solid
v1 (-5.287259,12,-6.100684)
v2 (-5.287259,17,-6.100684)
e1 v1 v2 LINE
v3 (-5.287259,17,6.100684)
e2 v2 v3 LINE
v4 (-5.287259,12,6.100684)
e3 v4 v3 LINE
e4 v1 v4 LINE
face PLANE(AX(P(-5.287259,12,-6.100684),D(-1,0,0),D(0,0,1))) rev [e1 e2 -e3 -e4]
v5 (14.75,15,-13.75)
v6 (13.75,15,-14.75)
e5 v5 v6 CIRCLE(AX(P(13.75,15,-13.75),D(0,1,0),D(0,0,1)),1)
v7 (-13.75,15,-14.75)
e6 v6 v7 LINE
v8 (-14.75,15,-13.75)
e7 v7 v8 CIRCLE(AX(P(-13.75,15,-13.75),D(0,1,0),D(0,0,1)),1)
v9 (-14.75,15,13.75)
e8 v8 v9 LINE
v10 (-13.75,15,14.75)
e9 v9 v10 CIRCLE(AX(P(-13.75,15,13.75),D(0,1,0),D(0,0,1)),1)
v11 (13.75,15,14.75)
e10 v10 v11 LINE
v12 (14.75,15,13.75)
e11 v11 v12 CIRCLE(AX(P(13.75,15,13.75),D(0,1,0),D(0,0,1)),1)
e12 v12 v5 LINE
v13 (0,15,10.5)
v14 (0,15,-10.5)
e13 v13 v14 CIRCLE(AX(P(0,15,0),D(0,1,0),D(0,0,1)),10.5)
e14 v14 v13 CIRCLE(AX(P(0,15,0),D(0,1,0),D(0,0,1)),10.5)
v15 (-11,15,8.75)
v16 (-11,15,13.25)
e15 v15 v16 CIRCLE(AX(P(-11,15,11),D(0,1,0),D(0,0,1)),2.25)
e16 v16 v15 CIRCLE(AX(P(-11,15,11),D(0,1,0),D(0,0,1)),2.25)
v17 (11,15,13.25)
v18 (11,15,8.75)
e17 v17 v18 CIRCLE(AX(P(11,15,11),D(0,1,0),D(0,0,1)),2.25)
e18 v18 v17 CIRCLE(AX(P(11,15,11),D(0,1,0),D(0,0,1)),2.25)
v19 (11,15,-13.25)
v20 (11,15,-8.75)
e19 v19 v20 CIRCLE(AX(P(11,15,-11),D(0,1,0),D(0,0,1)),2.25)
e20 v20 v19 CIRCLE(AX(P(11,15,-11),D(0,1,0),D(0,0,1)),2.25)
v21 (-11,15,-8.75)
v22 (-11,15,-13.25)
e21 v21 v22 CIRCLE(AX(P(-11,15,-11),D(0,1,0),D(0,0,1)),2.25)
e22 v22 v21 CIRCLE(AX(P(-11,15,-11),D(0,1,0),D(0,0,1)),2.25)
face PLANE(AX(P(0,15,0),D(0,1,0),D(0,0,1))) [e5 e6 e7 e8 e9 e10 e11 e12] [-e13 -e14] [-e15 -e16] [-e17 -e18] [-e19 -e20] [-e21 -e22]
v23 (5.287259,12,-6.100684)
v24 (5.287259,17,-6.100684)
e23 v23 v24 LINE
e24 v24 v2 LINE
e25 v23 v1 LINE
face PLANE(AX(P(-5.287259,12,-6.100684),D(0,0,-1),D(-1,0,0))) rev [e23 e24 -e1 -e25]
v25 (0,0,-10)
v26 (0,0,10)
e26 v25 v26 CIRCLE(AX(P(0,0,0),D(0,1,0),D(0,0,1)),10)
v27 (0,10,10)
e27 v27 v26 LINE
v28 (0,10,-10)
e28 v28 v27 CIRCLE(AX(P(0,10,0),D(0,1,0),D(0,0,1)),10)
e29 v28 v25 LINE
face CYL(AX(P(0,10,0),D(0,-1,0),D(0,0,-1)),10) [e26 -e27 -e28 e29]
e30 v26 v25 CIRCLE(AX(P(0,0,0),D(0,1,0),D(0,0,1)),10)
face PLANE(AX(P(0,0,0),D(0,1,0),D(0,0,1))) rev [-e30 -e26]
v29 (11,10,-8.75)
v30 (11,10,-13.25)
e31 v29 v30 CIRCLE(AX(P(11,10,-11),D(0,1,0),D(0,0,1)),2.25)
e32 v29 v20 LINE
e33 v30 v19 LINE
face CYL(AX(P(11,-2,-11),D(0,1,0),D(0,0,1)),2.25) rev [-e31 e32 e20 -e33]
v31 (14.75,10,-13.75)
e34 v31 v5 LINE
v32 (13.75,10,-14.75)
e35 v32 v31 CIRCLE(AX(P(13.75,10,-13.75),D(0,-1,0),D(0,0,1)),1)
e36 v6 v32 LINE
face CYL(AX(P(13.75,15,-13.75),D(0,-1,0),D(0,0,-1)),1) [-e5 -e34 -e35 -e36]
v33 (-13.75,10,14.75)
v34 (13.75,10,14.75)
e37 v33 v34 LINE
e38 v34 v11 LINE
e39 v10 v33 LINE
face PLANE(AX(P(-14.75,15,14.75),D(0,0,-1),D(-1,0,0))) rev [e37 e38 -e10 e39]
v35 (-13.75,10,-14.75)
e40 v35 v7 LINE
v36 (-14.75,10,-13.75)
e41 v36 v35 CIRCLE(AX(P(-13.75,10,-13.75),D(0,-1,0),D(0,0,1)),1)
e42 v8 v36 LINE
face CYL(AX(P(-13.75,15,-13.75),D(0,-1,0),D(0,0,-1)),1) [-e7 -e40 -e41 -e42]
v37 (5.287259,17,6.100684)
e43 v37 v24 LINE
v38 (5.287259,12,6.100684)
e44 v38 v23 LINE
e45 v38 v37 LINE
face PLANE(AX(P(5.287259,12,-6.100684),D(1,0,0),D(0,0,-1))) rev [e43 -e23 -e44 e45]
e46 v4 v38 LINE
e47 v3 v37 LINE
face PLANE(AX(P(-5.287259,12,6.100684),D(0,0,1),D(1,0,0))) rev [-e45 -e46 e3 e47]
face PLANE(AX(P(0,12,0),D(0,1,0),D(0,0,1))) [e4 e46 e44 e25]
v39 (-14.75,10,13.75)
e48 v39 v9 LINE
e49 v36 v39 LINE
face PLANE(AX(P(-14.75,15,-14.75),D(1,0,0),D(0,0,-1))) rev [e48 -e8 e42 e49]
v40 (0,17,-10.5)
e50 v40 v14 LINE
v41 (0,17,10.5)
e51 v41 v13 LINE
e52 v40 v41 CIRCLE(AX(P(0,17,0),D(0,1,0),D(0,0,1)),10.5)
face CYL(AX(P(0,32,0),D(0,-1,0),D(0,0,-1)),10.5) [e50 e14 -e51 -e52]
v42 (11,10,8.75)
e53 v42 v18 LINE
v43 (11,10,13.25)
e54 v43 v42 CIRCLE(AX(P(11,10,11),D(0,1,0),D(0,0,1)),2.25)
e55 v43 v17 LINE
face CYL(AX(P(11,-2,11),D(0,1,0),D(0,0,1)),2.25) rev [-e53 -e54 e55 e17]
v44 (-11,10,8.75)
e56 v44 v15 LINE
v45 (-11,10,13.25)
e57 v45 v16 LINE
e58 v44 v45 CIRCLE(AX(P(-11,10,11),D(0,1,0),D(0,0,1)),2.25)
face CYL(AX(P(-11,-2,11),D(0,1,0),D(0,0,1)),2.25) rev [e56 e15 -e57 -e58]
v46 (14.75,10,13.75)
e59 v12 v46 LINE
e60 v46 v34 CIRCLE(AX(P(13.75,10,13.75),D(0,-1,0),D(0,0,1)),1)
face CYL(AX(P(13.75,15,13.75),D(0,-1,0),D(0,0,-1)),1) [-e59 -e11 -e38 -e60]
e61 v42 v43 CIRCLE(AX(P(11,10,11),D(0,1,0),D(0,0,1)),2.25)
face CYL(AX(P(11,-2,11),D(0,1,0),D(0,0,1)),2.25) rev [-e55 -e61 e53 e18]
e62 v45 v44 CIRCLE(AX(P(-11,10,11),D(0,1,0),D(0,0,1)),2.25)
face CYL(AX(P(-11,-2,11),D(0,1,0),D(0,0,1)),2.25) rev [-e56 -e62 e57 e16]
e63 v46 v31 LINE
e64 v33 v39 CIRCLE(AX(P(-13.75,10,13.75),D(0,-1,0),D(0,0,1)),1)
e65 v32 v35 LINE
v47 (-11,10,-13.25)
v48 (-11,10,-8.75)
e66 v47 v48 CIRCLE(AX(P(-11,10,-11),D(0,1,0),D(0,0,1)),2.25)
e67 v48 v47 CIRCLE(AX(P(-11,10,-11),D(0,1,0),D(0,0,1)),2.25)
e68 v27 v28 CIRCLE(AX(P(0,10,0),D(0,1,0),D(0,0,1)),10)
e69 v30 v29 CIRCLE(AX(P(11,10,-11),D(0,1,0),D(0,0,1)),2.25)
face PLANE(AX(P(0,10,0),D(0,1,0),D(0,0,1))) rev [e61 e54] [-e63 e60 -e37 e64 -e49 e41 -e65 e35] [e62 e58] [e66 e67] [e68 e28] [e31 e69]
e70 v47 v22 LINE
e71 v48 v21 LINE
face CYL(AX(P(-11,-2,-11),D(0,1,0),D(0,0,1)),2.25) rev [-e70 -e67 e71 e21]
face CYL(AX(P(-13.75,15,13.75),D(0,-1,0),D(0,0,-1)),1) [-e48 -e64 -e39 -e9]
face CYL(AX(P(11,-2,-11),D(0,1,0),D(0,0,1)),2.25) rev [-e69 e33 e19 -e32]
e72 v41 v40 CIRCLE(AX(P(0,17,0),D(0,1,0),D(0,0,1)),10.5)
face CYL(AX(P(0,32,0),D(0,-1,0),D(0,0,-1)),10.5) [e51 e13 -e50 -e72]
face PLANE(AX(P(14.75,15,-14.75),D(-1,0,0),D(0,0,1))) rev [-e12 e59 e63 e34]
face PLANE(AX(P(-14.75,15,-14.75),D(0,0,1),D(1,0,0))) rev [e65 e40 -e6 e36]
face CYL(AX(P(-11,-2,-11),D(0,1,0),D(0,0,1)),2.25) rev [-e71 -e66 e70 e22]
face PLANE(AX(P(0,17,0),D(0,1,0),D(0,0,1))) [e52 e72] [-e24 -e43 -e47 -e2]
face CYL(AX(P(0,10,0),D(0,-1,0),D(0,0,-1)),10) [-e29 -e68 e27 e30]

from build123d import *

# Parameters (mm, degrees)
SKETCH_1_R          = 10
EXTRUDE_1_DEPTH     = 10
SKETCH_2_W          = 29.5
SKETCH_2_H          = 29.5
EXTRUDE_2_DEPTH     = 5
SKETCH_3_R          = 10.5
EXTRUDE_3_DEPTH     = 17
SKETCH_4_R          = 2.25
CUT_EXTRUDE_1_DEPTH = 17
FILLET_1_R          = 1
CUT_EXTRUDE_START   = -15
SKETCH_5_R          = 10.5
CUT_EXTRUDE_2_DEPTH = 15
SKETCH_6_W          = 10.574518314
SKETCH_6_H          = 12.201367284
CUT_EXTRUDE_3_DEPTH = 5


with BuildPart() as part:
    # 草图1 → 凸台-拉伸1 (new body)
    with BuildSketch(Plane(origin=(0, 0, 0), x_dir=(1, 0, 0), z_dir=(0, 1, 0))):
        with Locations(Location((0, 0, 0), (0, 0, 270))):
            Circle(SKETCH_1_R)
    extrude(amount=EXTRUDE_1_DEPTH)

    # 草图2 → 凸台-拉伸2 (add)
    with BuildSketch(Plane(origin=(0, 10, 0), x_dir=(1, 0, 0), z_dir=(0, 1, 0))):
        Rectangle(SKETCH_2_W, SKETCH_2_H)
    extrude(amount=EXTRUDE_2_DEPTH)

    # 草图3 → 凸台-拉伸3 (add)
    with BuildSketch(Plane(origin=(0, 15, 0), x_dir=(1, 0, 0), z_dir=(0, 1, 0))):
        with Locations(Location((0, 0, 0), (0, 0, 270))):
            Circle(SKETCH_3_R)
    extrude(amount=EXTRUDE_3_DEPTH)

    # 草图4 → 切除-拉伸1 (cut)
    with BuildSketch(Plane(origin=(0, 15, 0), x_dir=(1, 0, 0), z_dir=(0, 1, 0))):
        with Locations(Location((11, 11, 0), (0, 0, 270))):
            Circle(SKETCH_4_R)
        with Locations(Location((-11, 11, 0), (0, 0, 270))):
            Circle(SKETCH_4_R)
        with Locations(Location((-11, -11, 0), (0, 0, 270))):
            Circle(SKETCH_4_R)
        with Locations(Location((11, -11, 0), (0, 0, 270))):
            Circle(SKETCH_4_R)
    extrude(amount=-CUT_EXTRUDE_1_DEPTH, mode=Mode.SUBTRACT)

    # 圆角1
    fillet_1_edges = [part.edges().sort_by_distance(p)[0] for p in [
        (14.75, 12.5, 14.75),
        (14.75, 12.5, -14.75),
        (-14.75, 12.5, -14.75),
        (-14.75, 12.5, 14.75),
    ]]
    fillet(fillet_1_edges, radius=FILLET_1_R)

    # 草图5 → 切除-拉伸2 (cut)
    with BuildSketch(Plane(origin=(0, 32, 0), x_dir=(1, 0, 0), z_dir=(0, 1, 0)).offset(CUT_EXTRUDE_START)):
        with Locations(Location((0, 0, 0), (0, 0, 270))):
            Circle(SKETCH_5_R)
    extrude(amount=CUT_EXTRUDE_2_DEPTH, mode=Mode.SUBTRACT)

    # 草图6 → 切除-拉伸3 (cut)
    with BuildSketch(Plane(origin=(0, 17, 0), x_dir=(1, 0, 0), z_dir=(0, 1, 0))):
        Rectangle(SKETCH_6_W, SKETCH_6_H)
    extrude(amount=-CUT_EXTRUDE_3_DEPTH, mode=Mode.SUBTRACT)


solid = part.part
